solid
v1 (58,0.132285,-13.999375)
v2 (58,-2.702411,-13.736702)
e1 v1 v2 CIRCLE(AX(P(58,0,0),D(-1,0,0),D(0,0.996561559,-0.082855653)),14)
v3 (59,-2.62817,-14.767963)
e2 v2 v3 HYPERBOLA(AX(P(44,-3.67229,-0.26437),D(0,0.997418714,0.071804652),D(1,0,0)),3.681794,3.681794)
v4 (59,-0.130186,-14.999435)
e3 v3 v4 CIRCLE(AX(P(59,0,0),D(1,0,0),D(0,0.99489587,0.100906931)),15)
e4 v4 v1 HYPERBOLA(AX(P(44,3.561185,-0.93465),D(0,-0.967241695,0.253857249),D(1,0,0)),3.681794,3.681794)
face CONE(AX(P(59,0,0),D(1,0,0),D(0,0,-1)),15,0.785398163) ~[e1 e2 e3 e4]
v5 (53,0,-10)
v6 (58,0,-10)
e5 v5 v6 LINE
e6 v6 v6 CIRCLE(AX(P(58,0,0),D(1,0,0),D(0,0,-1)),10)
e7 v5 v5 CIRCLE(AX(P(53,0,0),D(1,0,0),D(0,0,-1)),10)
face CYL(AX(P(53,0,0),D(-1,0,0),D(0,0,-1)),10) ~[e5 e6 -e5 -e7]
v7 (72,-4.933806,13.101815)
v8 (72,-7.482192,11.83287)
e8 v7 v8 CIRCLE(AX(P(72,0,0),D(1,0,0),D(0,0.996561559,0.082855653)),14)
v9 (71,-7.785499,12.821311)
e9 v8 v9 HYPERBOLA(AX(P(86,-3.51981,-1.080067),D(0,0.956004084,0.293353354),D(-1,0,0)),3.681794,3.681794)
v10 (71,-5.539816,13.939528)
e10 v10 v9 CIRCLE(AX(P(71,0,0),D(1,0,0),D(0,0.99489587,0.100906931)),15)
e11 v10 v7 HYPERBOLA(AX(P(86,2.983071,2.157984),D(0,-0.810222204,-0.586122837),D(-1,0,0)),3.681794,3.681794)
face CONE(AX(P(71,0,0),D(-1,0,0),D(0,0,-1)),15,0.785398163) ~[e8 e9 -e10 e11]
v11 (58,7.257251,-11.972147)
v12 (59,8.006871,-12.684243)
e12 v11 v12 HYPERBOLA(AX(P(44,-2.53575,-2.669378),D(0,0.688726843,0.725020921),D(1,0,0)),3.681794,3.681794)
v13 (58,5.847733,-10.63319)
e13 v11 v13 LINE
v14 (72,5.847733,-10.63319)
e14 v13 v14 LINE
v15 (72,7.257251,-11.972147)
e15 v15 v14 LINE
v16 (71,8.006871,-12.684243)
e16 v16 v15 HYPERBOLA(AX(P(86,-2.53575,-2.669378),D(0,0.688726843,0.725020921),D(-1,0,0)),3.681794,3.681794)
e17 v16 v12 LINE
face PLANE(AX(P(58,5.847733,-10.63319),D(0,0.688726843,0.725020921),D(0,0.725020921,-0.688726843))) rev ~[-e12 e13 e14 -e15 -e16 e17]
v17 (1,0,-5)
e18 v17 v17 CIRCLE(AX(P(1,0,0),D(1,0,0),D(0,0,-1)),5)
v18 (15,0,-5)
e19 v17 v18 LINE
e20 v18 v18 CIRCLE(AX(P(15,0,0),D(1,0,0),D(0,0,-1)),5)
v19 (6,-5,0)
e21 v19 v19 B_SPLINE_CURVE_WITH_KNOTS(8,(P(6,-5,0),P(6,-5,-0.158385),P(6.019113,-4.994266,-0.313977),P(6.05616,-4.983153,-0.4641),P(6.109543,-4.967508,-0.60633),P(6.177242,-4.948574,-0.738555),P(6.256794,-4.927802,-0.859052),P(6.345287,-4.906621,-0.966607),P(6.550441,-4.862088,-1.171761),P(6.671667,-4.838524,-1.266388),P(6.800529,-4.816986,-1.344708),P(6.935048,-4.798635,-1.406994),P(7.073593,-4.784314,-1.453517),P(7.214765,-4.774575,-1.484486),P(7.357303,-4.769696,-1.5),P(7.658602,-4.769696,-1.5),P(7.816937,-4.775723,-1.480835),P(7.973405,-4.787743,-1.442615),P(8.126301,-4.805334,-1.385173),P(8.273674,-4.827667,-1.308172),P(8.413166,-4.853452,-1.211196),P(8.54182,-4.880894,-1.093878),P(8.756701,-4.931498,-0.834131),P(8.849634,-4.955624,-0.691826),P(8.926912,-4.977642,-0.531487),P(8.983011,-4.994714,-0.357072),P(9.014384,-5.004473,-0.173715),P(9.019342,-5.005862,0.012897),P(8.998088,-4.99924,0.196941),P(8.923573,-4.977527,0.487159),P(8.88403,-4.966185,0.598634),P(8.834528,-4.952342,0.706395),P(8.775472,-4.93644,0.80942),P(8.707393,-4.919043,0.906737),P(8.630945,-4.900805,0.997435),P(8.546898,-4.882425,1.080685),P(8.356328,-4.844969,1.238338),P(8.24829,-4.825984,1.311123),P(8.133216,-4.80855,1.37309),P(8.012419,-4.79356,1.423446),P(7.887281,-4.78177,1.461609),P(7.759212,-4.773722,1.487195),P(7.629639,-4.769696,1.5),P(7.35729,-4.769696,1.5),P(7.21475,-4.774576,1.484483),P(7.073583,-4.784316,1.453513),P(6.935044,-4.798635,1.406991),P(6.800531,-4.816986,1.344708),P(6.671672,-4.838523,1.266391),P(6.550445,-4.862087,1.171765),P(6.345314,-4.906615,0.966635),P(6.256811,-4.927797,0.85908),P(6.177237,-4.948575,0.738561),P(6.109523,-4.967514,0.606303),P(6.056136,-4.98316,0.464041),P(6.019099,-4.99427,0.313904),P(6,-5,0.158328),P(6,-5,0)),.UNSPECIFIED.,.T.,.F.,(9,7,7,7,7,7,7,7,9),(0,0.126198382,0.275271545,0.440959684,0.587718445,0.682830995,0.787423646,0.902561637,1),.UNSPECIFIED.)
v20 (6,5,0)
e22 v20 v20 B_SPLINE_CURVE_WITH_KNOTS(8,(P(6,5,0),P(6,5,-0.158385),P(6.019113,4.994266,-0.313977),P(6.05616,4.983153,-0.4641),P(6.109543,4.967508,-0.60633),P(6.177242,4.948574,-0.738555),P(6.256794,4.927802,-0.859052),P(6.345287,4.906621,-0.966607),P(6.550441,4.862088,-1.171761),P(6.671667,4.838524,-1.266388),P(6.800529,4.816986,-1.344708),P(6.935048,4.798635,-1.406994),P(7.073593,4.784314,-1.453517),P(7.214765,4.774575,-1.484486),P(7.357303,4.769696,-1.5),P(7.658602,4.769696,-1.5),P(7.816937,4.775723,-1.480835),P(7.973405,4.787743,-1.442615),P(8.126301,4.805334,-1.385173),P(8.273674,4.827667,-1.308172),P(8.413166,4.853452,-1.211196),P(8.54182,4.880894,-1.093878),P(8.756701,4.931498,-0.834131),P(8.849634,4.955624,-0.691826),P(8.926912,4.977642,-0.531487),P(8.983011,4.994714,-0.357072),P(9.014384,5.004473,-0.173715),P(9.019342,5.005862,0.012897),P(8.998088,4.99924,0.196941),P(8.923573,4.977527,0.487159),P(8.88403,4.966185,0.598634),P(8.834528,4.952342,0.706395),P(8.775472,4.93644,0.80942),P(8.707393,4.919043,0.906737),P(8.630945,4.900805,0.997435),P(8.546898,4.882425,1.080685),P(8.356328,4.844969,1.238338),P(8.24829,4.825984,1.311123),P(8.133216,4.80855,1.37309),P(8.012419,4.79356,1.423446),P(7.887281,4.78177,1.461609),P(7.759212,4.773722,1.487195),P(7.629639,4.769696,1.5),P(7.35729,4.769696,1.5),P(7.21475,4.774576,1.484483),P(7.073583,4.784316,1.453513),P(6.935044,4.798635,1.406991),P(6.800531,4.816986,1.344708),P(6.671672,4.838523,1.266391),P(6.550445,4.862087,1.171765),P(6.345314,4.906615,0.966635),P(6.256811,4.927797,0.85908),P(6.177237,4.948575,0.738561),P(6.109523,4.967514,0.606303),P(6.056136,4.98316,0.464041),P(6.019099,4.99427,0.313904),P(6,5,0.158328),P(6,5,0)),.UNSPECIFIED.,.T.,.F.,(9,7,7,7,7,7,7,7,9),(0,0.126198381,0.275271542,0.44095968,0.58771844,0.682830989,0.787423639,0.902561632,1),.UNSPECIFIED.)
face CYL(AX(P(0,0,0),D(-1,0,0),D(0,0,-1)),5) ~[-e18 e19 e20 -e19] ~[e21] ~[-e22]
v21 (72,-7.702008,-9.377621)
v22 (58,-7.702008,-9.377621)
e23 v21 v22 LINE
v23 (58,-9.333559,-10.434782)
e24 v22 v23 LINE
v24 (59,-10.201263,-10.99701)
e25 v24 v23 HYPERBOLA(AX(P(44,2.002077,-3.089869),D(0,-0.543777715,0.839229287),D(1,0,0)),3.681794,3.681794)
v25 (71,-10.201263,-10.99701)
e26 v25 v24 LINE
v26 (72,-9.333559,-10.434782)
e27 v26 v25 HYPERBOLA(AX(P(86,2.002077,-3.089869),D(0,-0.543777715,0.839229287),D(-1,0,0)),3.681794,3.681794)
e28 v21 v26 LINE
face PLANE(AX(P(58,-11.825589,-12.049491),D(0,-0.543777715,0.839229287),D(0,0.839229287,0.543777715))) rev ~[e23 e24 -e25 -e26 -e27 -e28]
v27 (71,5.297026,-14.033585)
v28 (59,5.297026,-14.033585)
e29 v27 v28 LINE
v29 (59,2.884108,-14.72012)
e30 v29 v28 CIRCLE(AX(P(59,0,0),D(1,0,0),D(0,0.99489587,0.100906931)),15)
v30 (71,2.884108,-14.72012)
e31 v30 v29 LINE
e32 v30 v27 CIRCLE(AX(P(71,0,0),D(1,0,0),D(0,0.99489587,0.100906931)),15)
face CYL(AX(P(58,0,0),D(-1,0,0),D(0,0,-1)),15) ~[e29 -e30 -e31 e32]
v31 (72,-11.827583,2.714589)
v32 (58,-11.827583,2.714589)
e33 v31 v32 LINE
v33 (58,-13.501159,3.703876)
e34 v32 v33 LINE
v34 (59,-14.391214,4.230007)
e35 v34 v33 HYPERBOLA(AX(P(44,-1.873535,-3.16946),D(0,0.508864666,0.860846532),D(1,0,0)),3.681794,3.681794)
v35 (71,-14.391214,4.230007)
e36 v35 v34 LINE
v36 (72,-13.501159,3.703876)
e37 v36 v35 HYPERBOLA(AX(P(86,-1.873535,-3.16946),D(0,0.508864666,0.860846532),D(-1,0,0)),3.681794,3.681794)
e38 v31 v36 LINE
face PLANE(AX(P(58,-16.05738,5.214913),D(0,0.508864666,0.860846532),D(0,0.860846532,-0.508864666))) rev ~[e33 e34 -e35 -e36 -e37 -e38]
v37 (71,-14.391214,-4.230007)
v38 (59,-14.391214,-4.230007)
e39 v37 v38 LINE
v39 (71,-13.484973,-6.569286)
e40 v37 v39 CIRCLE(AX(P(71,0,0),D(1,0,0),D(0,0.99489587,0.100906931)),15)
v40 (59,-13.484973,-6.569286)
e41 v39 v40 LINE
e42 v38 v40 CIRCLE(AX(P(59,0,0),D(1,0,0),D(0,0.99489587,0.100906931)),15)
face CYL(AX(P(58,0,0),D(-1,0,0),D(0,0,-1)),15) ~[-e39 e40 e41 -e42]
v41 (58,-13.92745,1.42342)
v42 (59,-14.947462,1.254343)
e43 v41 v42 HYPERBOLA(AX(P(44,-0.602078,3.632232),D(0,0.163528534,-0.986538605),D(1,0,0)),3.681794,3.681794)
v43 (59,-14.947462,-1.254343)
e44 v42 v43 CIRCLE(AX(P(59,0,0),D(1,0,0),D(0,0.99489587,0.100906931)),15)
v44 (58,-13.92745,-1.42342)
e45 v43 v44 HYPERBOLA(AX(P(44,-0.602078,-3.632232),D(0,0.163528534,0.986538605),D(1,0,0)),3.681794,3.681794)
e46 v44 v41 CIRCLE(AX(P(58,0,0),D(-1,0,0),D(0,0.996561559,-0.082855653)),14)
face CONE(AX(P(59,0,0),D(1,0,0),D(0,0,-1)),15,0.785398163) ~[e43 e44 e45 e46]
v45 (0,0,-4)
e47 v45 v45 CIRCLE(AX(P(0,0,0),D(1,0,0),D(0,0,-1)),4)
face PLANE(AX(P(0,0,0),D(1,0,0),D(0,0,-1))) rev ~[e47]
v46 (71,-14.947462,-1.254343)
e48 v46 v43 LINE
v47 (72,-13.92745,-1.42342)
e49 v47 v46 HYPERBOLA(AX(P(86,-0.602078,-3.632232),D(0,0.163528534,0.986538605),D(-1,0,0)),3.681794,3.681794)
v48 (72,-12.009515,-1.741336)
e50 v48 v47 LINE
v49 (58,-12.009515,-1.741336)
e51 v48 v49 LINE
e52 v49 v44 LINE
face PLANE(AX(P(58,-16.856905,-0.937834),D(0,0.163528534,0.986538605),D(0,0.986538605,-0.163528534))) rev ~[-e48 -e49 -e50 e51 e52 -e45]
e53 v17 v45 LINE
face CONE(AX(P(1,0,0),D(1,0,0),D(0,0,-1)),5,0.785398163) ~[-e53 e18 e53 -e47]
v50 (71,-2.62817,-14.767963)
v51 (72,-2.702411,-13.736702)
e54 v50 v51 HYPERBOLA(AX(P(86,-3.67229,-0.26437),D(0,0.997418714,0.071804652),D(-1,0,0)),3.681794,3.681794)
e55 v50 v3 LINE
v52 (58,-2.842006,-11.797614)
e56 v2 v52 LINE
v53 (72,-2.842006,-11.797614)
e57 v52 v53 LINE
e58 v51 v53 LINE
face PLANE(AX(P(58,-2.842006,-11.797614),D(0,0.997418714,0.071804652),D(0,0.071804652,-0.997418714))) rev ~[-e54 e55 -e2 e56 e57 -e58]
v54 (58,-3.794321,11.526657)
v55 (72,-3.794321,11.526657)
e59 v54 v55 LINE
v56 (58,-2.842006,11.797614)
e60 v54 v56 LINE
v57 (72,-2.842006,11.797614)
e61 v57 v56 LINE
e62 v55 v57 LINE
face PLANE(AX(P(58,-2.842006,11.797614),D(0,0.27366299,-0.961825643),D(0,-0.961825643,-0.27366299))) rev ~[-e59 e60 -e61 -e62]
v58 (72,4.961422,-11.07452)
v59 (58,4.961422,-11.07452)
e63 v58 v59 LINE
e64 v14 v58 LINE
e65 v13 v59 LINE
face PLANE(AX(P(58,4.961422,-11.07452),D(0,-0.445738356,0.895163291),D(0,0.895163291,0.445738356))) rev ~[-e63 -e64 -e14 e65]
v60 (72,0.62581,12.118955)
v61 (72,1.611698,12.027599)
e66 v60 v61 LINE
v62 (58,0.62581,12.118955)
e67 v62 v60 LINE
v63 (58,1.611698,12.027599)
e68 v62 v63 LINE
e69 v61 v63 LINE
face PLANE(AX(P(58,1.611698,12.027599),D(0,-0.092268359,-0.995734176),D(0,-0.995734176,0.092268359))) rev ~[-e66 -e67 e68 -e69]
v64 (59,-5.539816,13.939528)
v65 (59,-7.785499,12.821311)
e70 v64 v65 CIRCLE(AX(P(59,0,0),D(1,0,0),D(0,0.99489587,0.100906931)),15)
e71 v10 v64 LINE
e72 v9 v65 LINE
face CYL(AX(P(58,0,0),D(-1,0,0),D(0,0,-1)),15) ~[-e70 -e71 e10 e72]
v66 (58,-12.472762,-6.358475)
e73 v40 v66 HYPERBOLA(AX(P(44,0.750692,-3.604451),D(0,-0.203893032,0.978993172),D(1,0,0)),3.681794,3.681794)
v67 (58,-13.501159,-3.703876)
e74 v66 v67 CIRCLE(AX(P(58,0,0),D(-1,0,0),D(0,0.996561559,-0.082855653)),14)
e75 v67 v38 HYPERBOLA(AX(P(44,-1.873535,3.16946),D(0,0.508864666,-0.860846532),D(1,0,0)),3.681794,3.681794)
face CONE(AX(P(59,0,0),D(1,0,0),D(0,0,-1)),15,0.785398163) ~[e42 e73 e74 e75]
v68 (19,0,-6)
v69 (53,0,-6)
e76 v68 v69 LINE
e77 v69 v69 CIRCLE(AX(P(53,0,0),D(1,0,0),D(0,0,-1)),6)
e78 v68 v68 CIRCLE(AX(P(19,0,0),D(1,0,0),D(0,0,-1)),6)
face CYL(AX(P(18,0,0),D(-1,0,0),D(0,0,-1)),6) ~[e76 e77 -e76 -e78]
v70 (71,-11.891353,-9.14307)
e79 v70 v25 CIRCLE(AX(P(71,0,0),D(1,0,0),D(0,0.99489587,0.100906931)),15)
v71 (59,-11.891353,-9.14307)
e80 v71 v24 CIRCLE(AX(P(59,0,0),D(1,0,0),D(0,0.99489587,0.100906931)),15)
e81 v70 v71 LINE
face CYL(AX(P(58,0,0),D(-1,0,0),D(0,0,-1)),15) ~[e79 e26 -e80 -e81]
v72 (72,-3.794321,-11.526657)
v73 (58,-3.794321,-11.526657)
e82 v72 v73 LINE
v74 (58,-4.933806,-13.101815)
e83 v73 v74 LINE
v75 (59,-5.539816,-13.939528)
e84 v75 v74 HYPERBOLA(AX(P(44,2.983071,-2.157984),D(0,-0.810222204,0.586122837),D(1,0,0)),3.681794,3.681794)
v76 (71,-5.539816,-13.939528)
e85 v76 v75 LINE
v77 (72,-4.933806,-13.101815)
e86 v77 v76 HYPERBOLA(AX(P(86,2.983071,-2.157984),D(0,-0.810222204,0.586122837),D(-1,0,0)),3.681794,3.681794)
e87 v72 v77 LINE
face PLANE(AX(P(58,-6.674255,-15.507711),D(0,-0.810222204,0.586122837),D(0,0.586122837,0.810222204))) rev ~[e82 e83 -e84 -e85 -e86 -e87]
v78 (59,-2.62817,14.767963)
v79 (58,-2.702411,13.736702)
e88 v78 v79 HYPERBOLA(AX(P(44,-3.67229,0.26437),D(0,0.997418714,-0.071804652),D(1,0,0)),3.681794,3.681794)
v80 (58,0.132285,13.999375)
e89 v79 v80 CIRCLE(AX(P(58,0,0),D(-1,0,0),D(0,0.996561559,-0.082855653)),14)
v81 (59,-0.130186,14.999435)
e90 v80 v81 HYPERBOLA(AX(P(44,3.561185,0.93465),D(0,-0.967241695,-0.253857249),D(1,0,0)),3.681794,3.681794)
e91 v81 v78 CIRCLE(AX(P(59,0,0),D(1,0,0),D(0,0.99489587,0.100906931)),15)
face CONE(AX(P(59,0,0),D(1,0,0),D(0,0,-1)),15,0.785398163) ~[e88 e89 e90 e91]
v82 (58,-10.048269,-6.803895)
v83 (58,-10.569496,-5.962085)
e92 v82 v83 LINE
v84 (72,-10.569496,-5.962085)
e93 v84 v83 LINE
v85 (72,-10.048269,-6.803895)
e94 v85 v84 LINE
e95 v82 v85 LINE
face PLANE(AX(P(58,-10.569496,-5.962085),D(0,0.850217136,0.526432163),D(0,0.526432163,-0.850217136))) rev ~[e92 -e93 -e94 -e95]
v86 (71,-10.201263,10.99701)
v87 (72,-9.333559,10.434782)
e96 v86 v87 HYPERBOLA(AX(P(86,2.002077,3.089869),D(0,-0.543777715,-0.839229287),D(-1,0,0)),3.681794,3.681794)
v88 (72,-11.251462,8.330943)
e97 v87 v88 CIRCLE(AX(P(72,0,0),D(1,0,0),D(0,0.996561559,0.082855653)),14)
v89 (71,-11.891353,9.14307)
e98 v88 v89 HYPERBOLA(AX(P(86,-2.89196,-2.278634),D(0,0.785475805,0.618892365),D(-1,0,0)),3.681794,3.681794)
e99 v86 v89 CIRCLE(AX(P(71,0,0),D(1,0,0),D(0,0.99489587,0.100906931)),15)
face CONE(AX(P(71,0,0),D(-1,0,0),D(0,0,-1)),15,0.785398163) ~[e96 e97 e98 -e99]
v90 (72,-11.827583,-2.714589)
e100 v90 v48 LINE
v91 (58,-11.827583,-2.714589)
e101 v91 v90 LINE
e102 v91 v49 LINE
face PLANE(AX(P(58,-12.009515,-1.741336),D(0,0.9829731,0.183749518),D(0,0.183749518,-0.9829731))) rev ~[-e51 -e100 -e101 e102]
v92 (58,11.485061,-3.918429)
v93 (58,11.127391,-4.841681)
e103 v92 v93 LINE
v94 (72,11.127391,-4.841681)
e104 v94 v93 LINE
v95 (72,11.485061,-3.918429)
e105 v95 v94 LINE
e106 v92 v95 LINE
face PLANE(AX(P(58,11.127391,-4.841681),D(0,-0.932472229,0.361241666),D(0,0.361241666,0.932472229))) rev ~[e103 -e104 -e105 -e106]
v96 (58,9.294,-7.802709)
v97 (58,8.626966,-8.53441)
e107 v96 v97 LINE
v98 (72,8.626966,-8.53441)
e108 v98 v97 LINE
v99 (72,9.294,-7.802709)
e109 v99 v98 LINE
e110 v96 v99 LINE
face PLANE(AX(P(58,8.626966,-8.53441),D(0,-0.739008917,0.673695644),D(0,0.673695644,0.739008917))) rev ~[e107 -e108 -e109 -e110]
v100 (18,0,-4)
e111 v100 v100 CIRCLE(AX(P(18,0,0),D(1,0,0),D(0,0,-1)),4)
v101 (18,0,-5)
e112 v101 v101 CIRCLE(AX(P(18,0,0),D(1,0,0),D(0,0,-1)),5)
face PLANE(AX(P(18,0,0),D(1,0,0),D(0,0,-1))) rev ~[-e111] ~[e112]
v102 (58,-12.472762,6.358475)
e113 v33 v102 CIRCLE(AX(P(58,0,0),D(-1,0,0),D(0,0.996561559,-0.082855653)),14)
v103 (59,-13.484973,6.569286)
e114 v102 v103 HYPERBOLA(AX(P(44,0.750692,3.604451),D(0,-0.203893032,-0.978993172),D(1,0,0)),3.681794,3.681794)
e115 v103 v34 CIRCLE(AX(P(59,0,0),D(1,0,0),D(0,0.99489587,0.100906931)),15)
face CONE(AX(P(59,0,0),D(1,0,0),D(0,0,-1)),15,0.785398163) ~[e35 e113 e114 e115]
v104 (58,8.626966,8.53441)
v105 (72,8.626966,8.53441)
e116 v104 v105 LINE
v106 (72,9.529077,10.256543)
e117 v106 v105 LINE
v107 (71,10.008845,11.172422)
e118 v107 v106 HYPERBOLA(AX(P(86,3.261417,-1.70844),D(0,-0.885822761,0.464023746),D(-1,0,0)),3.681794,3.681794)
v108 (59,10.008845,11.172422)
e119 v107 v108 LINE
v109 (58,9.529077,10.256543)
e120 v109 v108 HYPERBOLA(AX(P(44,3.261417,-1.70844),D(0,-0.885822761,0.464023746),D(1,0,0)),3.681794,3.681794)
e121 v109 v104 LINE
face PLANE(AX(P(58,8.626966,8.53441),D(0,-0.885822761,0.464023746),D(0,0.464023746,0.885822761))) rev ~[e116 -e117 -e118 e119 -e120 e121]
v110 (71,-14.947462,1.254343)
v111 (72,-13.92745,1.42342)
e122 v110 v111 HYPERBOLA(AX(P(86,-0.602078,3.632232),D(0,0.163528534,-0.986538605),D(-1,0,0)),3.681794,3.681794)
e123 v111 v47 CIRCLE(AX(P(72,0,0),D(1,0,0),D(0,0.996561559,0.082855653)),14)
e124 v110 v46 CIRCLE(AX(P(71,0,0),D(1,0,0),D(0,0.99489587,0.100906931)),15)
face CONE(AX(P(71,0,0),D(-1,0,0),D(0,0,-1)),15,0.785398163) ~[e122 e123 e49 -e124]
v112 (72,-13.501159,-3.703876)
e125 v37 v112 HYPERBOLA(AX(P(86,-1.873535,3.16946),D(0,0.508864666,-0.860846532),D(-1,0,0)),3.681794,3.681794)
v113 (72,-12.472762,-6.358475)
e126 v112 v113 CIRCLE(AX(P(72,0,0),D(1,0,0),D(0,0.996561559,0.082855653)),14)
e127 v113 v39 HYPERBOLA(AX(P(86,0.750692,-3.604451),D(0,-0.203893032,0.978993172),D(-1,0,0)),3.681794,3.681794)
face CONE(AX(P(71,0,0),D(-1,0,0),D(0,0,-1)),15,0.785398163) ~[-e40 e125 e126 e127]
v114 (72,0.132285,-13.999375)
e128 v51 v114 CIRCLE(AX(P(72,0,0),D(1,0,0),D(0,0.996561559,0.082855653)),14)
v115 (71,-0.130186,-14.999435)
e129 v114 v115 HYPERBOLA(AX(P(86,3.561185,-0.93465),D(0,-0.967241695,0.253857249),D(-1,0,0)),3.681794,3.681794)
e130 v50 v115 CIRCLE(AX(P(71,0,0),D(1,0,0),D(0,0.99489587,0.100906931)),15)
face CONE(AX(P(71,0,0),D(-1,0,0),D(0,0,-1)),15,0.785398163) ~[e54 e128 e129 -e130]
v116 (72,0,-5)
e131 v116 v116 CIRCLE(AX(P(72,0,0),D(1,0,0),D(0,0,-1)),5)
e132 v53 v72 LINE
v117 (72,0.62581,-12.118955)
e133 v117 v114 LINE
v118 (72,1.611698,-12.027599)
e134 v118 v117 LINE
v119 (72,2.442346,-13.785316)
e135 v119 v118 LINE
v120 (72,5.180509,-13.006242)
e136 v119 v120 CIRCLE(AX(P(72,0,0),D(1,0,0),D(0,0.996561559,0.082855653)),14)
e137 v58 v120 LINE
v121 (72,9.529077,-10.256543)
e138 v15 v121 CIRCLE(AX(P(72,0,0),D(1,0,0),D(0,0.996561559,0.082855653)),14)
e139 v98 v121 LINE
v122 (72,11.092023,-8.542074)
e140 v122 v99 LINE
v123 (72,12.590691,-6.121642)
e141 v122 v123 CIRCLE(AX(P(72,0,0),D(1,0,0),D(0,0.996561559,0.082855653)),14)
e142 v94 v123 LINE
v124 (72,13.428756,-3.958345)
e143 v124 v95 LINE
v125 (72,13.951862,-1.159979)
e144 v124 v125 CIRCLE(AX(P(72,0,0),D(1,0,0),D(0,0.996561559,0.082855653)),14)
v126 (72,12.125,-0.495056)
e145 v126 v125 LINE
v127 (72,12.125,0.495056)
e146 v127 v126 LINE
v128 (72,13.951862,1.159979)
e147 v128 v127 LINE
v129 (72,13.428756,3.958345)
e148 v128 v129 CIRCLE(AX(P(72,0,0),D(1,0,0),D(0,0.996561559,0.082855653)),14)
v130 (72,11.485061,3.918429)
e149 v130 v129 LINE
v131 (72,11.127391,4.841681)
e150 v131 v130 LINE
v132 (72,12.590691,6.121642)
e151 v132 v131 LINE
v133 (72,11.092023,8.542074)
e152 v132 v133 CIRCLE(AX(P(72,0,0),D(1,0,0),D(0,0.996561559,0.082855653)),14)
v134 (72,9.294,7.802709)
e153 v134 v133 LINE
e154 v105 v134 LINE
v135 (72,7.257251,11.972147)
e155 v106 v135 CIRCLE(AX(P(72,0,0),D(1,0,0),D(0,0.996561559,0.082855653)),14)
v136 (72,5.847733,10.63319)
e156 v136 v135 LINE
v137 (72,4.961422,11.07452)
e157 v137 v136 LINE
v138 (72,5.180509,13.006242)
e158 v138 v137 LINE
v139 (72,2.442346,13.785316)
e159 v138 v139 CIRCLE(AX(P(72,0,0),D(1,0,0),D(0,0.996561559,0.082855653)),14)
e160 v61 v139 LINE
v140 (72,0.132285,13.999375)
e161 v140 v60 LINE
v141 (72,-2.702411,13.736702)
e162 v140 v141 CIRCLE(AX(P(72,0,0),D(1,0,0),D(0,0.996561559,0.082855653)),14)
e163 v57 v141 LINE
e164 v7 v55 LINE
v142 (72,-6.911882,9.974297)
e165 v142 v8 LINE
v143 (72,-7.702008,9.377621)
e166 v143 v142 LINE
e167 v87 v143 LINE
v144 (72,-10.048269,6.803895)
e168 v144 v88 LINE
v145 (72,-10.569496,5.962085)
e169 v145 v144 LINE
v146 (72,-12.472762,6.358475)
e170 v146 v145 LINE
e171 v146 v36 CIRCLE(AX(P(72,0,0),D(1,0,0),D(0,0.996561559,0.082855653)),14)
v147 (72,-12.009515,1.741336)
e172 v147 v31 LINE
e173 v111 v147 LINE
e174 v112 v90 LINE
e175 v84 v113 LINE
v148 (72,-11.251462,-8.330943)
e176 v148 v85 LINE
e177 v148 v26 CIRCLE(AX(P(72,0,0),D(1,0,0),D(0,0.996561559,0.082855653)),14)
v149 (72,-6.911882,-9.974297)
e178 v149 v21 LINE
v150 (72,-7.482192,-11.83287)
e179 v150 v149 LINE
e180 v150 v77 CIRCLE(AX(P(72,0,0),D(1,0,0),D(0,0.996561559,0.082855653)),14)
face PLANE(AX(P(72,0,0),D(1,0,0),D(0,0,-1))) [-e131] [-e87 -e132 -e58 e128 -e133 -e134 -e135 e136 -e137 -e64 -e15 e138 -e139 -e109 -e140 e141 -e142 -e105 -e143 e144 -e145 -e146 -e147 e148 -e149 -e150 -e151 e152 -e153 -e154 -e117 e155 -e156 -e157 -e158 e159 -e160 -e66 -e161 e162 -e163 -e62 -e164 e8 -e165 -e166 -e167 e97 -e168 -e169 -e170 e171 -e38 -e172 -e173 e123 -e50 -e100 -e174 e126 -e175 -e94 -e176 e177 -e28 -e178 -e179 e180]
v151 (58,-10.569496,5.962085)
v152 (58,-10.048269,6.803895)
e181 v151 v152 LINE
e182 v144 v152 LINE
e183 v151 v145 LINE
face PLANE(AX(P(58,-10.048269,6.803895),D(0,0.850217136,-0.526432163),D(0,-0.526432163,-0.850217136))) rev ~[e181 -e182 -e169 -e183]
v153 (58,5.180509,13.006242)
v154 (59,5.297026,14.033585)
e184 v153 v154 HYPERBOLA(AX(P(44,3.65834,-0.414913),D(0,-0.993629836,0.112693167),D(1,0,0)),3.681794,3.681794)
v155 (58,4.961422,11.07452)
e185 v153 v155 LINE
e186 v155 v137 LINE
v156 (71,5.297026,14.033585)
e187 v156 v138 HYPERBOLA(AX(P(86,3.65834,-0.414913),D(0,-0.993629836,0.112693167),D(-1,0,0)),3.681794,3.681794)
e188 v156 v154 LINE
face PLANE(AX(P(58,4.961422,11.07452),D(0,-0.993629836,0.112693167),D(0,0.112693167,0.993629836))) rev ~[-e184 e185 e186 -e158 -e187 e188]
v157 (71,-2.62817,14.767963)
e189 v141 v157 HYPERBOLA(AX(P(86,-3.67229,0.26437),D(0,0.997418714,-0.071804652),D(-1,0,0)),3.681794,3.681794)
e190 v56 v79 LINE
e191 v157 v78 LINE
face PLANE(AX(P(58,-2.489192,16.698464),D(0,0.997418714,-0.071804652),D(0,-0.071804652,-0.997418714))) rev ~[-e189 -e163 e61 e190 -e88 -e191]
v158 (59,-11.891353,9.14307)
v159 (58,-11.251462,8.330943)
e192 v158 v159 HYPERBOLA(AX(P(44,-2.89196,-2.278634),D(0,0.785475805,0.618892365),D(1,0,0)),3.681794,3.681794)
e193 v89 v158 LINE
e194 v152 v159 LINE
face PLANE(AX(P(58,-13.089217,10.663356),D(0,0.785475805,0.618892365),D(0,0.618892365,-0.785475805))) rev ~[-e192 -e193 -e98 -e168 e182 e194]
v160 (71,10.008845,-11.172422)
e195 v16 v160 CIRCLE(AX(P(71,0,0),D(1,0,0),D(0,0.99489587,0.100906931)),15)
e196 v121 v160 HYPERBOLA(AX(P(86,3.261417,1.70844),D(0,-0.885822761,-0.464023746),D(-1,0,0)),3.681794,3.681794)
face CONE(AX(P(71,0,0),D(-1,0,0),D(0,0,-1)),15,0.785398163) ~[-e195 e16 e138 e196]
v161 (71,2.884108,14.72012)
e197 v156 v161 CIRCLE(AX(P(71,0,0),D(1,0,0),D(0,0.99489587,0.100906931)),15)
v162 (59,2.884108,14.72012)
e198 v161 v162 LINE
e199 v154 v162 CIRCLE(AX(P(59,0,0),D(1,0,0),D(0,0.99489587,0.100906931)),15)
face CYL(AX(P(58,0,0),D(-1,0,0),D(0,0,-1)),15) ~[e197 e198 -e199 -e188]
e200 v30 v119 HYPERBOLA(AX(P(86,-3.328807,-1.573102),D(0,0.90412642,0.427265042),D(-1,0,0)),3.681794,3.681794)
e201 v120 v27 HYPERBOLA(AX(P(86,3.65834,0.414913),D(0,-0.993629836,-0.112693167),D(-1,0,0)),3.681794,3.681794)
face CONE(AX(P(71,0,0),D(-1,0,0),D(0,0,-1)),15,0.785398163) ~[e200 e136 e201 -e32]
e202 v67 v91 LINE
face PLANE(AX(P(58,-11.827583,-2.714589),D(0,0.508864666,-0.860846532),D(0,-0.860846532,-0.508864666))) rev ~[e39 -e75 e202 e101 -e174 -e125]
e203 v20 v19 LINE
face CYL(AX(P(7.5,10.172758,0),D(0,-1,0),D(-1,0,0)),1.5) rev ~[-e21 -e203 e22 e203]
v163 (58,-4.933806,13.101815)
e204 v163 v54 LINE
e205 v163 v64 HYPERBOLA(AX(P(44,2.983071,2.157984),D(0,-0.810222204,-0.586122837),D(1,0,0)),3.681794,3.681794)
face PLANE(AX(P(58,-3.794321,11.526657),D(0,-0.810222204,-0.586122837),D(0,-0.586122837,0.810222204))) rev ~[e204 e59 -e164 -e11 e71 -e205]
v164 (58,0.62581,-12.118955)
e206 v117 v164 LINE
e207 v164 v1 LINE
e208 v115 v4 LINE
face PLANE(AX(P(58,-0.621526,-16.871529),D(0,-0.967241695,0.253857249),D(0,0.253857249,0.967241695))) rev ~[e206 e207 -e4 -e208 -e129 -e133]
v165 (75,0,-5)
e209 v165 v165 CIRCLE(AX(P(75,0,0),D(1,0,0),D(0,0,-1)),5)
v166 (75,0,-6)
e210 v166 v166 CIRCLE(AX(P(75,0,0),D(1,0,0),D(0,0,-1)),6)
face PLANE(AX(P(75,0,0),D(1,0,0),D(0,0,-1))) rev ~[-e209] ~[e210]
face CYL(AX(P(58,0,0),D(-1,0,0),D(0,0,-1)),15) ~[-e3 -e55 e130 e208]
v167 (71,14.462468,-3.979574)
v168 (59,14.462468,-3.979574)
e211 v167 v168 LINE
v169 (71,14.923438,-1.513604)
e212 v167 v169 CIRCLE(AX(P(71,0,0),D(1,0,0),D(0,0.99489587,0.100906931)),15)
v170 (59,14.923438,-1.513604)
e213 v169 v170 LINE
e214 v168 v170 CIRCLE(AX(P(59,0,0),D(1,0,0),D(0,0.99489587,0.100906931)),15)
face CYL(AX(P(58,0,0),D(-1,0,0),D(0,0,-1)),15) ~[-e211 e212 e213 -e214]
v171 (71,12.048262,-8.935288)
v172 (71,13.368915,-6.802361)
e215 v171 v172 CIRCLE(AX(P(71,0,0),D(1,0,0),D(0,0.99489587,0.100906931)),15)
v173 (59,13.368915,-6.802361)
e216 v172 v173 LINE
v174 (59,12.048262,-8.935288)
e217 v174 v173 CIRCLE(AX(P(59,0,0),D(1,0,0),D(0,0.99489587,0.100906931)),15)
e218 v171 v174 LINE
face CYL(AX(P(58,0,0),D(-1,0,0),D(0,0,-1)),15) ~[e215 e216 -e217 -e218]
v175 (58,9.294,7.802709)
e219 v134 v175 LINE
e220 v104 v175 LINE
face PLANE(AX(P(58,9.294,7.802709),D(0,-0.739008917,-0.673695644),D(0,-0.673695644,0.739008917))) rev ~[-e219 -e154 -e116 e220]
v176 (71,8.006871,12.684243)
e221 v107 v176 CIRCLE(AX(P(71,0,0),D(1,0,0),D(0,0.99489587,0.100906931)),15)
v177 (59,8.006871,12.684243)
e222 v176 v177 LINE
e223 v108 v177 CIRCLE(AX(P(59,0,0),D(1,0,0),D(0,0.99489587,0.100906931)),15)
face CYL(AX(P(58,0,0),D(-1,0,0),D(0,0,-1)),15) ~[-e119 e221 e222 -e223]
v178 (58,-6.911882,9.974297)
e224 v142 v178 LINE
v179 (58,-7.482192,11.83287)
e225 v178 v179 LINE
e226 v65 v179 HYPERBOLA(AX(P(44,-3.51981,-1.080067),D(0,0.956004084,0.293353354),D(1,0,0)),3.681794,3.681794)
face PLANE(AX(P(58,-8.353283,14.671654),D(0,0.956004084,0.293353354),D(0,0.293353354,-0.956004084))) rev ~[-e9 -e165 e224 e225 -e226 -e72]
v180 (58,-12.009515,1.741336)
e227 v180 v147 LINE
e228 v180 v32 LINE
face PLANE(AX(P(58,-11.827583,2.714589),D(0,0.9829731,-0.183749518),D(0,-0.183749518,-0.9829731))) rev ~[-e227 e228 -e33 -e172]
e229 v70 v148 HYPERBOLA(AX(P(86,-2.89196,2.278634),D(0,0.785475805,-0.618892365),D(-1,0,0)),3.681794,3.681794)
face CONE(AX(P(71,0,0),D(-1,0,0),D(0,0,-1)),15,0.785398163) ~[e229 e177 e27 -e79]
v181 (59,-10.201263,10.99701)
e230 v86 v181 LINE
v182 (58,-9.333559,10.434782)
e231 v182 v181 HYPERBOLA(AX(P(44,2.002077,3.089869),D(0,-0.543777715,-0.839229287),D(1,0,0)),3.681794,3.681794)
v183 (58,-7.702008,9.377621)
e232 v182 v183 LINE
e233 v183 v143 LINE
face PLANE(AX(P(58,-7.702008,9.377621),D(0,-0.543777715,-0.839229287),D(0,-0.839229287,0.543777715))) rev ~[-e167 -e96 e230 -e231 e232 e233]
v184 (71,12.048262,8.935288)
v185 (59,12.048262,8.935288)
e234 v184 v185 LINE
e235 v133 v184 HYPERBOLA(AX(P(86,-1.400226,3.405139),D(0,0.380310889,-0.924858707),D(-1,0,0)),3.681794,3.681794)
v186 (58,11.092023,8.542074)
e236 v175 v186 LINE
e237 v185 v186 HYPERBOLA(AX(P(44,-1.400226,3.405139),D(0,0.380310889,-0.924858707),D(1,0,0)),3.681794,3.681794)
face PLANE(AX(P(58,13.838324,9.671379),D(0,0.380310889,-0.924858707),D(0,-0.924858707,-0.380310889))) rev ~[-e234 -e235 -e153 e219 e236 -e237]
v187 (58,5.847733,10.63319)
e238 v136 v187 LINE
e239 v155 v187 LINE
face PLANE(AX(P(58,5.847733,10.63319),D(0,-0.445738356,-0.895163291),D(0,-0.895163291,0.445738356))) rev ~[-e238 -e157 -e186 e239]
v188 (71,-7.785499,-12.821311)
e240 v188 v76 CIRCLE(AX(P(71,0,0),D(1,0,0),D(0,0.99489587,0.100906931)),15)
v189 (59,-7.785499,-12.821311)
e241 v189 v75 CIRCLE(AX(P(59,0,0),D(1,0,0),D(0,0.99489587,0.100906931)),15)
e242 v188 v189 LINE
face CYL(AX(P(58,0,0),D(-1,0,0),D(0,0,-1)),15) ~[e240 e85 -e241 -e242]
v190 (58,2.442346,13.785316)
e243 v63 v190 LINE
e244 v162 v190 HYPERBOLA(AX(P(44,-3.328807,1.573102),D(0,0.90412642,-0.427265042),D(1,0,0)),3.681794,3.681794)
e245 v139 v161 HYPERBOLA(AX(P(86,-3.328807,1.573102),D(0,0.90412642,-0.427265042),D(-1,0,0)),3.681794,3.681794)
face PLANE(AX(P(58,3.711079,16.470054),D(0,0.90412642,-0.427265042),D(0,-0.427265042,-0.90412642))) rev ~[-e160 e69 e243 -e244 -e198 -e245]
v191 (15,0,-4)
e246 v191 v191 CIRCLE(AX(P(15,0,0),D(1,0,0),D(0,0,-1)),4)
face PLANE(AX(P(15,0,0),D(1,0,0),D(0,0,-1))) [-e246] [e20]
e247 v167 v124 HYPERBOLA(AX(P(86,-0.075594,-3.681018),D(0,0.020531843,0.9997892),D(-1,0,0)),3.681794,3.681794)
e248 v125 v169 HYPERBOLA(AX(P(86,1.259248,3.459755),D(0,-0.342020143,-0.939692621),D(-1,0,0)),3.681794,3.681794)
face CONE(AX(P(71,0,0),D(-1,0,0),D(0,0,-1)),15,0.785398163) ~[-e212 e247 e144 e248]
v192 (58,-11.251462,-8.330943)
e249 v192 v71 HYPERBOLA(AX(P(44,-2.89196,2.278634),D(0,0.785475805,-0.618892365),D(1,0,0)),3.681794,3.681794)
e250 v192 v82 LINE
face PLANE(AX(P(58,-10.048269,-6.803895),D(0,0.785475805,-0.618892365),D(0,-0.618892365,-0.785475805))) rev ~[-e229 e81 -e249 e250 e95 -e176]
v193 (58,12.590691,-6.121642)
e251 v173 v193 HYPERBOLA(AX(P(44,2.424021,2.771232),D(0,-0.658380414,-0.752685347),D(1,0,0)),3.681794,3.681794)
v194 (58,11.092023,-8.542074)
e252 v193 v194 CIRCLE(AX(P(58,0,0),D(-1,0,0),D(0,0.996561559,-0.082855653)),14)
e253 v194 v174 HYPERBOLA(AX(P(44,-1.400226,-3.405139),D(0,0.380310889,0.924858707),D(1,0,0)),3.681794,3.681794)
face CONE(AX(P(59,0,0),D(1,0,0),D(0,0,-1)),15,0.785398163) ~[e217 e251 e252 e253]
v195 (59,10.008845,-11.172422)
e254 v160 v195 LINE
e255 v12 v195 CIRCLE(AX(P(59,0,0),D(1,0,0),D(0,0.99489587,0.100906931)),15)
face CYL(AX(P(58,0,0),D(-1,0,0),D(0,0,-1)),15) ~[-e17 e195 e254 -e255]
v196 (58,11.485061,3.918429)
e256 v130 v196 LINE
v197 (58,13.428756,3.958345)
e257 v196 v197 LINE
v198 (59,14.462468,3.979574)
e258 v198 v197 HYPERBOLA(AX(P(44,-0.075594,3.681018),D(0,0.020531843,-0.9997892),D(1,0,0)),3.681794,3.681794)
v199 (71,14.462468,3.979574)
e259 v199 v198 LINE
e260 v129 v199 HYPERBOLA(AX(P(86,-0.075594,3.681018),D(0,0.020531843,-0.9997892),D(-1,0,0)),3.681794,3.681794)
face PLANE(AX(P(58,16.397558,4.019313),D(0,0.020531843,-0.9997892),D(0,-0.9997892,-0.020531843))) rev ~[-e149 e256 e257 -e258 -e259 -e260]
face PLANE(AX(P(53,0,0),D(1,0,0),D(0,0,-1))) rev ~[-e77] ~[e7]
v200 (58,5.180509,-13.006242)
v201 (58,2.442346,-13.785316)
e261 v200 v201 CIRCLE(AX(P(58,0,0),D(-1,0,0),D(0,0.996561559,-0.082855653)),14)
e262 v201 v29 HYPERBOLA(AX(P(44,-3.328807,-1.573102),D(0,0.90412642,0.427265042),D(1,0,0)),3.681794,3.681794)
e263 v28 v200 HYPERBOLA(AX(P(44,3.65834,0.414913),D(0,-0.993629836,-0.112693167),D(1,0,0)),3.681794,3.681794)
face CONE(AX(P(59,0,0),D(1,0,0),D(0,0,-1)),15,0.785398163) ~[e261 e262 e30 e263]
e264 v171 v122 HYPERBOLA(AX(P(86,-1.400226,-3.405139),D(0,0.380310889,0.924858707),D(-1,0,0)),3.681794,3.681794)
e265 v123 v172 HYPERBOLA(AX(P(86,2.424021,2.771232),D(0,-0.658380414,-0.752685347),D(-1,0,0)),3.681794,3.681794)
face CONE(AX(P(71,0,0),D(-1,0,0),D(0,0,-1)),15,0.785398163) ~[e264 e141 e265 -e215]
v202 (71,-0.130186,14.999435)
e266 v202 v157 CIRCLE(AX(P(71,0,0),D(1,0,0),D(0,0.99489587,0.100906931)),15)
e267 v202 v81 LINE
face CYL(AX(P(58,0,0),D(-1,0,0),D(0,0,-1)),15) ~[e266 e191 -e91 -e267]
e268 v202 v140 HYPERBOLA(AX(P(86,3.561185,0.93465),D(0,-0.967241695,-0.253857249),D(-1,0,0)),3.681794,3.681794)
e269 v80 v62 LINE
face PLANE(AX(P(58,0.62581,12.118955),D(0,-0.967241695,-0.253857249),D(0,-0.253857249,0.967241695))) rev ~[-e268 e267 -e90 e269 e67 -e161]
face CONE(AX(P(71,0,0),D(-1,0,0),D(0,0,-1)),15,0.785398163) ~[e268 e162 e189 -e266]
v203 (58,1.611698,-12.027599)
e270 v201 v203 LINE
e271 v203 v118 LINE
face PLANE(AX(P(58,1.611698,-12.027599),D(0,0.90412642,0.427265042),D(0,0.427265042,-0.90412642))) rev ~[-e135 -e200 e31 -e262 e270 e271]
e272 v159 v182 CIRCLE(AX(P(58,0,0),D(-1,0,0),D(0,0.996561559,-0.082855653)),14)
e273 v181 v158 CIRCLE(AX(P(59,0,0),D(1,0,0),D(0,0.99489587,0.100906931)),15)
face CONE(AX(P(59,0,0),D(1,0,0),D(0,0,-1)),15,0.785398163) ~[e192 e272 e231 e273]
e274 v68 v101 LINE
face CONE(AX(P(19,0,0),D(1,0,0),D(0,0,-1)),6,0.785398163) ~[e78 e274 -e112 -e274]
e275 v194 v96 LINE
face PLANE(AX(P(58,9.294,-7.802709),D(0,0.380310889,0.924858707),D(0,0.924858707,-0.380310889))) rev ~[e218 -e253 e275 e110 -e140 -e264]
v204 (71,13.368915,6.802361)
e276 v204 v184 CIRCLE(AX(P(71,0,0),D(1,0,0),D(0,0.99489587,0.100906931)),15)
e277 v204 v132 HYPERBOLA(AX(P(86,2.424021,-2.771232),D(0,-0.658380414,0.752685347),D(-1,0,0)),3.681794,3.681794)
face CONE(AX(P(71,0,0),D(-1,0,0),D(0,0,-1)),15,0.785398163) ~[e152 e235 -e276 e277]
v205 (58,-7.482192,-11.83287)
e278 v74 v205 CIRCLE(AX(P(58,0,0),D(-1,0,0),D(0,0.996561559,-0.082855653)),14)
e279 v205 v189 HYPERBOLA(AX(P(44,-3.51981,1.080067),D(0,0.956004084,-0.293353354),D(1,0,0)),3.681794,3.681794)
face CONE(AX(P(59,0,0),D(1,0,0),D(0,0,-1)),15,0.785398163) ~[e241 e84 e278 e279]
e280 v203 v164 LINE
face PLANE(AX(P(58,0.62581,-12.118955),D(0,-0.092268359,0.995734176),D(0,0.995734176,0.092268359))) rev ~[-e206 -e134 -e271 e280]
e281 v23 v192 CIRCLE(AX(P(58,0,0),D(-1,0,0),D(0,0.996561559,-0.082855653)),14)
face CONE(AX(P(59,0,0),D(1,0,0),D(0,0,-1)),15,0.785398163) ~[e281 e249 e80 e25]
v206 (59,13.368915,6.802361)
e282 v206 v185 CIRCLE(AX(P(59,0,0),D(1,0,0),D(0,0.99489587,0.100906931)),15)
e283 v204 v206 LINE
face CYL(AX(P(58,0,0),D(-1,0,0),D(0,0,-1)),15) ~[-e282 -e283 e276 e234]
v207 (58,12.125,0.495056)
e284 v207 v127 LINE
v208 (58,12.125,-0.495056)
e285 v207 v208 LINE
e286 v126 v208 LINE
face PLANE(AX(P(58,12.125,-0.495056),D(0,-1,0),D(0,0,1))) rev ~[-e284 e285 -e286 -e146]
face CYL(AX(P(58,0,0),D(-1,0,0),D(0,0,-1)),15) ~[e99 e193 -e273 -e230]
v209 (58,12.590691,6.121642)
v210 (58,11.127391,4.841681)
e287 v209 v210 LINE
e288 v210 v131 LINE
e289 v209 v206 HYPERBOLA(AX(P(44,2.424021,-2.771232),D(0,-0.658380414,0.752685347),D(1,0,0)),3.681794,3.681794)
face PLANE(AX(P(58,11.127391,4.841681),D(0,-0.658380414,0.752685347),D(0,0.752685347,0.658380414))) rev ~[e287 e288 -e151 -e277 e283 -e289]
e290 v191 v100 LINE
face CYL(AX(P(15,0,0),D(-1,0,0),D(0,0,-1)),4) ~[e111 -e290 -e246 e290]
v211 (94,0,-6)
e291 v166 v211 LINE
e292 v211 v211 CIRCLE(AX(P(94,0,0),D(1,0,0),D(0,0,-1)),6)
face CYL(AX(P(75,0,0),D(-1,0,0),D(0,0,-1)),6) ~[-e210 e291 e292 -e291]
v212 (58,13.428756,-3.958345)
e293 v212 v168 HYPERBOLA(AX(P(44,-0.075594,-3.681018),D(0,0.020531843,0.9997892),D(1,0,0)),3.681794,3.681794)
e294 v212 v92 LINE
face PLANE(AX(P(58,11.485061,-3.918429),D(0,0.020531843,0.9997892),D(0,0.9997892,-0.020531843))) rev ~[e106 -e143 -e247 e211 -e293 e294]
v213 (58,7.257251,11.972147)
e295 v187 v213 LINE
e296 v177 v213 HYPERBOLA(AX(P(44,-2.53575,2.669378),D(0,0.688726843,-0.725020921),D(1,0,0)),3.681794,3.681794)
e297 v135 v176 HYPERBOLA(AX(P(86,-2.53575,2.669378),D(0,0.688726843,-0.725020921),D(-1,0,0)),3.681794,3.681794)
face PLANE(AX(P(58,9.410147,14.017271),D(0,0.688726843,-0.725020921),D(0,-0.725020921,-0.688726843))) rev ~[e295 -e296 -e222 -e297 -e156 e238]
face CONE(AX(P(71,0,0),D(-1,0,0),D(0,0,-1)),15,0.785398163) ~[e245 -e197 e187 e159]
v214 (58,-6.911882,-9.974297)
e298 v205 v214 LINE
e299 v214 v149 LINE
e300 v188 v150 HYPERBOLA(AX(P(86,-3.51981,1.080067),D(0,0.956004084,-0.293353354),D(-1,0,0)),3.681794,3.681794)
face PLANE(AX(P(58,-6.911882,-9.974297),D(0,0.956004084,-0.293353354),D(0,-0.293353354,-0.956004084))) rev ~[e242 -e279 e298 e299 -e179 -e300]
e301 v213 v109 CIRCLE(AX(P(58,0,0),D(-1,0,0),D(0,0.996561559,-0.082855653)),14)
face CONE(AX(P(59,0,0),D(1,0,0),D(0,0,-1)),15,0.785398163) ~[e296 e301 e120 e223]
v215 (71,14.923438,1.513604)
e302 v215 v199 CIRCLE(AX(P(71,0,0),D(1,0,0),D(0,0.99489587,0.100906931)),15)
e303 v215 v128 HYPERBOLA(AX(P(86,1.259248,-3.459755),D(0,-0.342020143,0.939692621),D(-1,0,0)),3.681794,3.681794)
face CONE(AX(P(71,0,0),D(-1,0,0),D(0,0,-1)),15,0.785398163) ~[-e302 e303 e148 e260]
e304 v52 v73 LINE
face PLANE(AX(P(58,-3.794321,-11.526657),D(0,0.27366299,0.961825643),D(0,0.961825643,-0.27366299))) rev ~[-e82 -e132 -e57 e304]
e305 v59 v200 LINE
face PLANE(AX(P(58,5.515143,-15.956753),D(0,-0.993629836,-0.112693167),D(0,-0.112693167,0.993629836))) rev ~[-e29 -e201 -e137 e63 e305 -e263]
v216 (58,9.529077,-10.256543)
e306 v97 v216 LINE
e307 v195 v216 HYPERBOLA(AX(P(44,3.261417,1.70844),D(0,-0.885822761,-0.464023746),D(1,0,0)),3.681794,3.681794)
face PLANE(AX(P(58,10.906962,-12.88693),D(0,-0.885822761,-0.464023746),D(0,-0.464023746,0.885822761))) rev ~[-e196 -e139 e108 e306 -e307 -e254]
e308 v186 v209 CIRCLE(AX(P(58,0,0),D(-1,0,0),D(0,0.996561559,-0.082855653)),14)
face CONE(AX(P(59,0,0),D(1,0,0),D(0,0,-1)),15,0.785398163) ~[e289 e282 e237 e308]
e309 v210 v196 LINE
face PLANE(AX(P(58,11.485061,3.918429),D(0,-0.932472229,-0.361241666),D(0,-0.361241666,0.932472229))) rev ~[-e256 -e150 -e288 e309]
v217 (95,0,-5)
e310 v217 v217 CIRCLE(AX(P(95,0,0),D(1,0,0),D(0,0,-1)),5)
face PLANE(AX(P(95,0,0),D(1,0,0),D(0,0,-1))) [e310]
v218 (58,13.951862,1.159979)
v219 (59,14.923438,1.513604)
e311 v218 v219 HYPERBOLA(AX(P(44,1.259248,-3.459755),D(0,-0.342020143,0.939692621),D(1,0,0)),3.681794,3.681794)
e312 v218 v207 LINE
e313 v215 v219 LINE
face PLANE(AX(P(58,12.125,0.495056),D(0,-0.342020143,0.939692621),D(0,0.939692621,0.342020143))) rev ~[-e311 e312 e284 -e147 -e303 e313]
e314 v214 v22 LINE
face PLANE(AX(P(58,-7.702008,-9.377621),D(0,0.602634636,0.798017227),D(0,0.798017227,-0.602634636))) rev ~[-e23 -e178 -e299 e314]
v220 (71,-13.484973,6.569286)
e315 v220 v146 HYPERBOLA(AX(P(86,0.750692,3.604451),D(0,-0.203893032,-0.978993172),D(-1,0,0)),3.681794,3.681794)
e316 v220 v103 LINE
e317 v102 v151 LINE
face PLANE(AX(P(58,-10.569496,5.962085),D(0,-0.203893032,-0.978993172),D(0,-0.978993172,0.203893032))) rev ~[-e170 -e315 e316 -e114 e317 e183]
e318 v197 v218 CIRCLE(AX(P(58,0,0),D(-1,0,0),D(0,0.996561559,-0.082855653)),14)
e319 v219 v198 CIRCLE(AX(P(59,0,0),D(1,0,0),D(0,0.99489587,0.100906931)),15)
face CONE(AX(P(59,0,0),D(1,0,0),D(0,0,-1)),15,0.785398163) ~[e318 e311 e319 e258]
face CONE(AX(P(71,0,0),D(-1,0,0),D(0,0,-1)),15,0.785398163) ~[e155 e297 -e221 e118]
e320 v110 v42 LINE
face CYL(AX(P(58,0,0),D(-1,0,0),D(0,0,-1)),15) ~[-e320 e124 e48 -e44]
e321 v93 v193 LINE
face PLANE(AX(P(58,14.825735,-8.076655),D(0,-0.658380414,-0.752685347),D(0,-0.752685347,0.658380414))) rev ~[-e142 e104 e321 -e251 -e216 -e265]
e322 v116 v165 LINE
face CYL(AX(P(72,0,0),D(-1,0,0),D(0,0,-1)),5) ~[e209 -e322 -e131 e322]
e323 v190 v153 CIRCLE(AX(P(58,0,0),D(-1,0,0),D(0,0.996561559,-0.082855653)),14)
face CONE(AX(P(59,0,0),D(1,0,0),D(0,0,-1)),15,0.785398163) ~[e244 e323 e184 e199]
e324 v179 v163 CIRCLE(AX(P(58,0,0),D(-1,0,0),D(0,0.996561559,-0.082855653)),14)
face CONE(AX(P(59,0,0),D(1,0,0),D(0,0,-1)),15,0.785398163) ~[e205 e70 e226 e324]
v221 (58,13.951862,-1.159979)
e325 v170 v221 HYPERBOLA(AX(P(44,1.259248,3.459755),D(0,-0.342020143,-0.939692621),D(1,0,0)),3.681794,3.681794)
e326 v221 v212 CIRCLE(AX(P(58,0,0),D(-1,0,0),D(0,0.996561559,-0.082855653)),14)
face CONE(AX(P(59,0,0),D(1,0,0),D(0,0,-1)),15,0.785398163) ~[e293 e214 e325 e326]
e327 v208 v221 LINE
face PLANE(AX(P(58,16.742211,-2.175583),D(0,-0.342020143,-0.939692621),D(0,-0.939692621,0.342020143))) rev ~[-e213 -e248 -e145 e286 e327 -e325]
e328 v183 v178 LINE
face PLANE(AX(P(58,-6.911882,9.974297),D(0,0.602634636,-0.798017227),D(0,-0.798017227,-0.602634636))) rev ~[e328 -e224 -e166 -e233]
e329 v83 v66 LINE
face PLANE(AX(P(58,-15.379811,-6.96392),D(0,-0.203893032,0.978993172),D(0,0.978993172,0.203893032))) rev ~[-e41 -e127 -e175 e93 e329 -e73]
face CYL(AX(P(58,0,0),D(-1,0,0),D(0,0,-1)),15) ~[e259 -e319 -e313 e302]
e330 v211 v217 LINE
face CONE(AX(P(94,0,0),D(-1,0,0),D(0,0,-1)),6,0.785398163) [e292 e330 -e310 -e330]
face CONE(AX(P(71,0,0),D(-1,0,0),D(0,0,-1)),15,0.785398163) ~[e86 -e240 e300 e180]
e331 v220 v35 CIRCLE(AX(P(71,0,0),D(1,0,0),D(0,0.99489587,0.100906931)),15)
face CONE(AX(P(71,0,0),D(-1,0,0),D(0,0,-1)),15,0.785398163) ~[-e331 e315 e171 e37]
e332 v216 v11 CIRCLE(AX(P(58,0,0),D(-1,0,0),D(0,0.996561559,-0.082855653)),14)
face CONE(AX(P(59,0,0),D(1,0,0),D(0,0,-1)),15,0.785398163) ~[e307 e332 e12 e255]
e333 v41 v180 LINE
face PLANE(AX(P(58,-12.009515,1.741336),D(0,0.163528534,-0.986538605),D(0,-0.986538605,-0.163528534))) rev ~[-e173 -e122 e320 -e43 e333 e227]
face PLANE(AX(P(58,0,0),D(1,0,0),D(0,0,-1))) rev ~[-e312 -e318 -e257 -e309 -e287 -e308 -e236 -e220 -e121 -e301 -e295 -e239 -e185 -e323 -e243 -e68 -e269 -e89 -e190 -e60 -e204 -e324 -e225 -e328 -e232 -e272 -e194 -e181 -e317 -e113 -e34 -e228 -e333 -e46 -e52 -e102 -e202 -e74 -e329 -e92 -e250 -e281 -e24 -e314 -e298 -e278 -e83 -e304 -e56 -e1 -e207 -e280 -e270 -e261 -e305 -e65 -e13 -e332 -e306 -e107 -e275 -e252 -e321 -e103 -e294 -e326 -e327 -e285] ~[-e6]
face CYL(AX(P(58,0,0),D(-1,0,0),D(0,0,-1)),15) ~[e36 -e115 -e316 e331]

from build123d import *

# Parameters (mm, degrees)
SKETCH1_R            = 5
BOSS_EXTRUDE1_DEPTH  = 15
SKETCH2_R            = 4
BOSS_EXTRUDE2_DEPTH  = 3
SKETCH3_R            = 6
BOSS_EXTRUDE3_DEPTH  = 35
SKETCH4_R            = 10
BOSS_EXTRUDE4_DEPTH  = 5
SKETCH5_R            = 15
BOSS_EXTRUDE5_DEPTH  = 14
SKETCH6_R            = 5
BOSS_EXTRUDE6_DEPTH  = 3
SKETCH7_R            = 6
BOSS_EXTRUDE7_DEPTH  = 20
CHAMFER1_SIZE        = 1
CUT_EXTRUDE1_DEPTH   = 62.757590627
CIRPATTERN1_COUNT    = 17
CUT_SWEEP1_PROFILE_R = 1.5


with BuildPart() as part:
    # Sketch1 → Boss-Extrude1 (new body)
    with BuildSketch(Plane(origin=(0, 0, 0), x_dir=(0, 0, -1), z_dir=(1, 0, 0))):
        Circle(SKETCH1_R)
    extrude(amount=BOSS_EXTRUDE1_DEPTH)

    # Sketch2 → Boss-Extrude2 (add)
    with BuildSketch(Plane(origin=(15, 0, 0), x_dir=(0, 0, -1), z_dir=(1, 0, 0))):
        Circle(SKETCH2_R)
    extrude(amount=BOSS_EXTRUDE2_DEPTH)

    # Sketch3 → Boss-Extrude3 (add)
    with BuildSketch(Plane(origin=(18, 0, 0), x_dir=(0, 0, -1), z_dir=(1, 0, 0))):
        Circle(SKETCH3_R)
    extrude(amount=BOSS_EXTRUDE3_DEPTH)

    # Sketch4 → Boss-Extrude4 (add)
    with BuildSketch(Plane(origin=(53, 0, 0), x_dir=(0, 0, -1), z_dir=(1, 0, 0))):
        Circle(SKETCH4_R)
    extrude(amount=BOSS_EXTRUDE4_DEPTH)

    # Sketch5 → Boss-Extrude5 (add)
    with BuildSketch(Plane(origin=(58, 0, 0), x_dir=(0, 0, -1), z_dir=(1, 0, 0))):
        Circle(SKETCH5_R)
    extrude(amount=BOSS_EXTRUDE5_DEPTH)

    # Sketch6 → Boss-Extrude6 (add)
    with BuildSketch(Plane(origin=(72, 0, 0), x_dir=(0, 0, -1), z_dir=(1, 0, 0))):
        Circle(SKETCH6_R)
    extrude(amount=BOSS_EXTRUDE6_DEPTH)

    # Sketch7 → Boss-Extrude7 (add)
    with BuildSketch(Plane(origin=(75, 0, 0), x_dir=(0, 0, -1), z_dir=(1, 0, 0))):
        Circle(SKETCH7_R)
    extrude(amount=BOSS_EXTRUDE7_DEPTH)

    # Chamfer1
    chamfer1_edges = [part.edges().sort_by_distance(p)[0] for p in [
        (18, 0, 6),
        (58, 0, 15),
        (72, 0, 15),
        (0, 0, 5),
        (95, 0, 6),
    ]]
    chamfer(chamfer1_edges, length=CHAMFER1_SIZE)

    # Sketch8 → Cut-Extrude1 (cut, symmetric)
    with BuildSketch(Plane.ZY.offset(-58)):
        Polygon((2.175583012, 16.742210538), (-2.175583012, 16.742210538), (-0.495055811, 12.125), (0.495055811, 12.125), align=None)
    cut_extrude1 = extrude(amount=CUT_EXTRUDE1_DEPTH, both=True, mode=Mode.SUBTRACT)

    # CirPattern1: Cut-Extrude1 ×17 about axis
    cirpattern1_axis = Axis((0, 0, 0), (1, 0, 0))
    for i in range(1, CIRPATTERN1_COUNT):
        add(cut_extrude1.rotate(cirpattern1_axis, i * 360 / CIRPATTERN1_COUNT), mode=Mode.SUBTRACT)

    # Cut-Sweep1: sweep along a path in Sketch9
    with BuildLine(Plane.XY) as cut_sweep1_path:
        Line((7.5, 10.172757983), (7.5, -6.529018922))
    # Cut-Sweep1 profile (on start of the path) → Cut-Sweep1 (sweep, cut)
    with BuildSketch(Plane(origin=(7.5, 10.172757983, 0), x_dir=(-1, 0, 0), z_dir=(0, -1, 0))):
        Circle(CUT_SWEEP1_PROFILE_R)
    sweep(path=cut_sweep1_path.line, mode=Mode.SUBTRACT)


solid = part.part
